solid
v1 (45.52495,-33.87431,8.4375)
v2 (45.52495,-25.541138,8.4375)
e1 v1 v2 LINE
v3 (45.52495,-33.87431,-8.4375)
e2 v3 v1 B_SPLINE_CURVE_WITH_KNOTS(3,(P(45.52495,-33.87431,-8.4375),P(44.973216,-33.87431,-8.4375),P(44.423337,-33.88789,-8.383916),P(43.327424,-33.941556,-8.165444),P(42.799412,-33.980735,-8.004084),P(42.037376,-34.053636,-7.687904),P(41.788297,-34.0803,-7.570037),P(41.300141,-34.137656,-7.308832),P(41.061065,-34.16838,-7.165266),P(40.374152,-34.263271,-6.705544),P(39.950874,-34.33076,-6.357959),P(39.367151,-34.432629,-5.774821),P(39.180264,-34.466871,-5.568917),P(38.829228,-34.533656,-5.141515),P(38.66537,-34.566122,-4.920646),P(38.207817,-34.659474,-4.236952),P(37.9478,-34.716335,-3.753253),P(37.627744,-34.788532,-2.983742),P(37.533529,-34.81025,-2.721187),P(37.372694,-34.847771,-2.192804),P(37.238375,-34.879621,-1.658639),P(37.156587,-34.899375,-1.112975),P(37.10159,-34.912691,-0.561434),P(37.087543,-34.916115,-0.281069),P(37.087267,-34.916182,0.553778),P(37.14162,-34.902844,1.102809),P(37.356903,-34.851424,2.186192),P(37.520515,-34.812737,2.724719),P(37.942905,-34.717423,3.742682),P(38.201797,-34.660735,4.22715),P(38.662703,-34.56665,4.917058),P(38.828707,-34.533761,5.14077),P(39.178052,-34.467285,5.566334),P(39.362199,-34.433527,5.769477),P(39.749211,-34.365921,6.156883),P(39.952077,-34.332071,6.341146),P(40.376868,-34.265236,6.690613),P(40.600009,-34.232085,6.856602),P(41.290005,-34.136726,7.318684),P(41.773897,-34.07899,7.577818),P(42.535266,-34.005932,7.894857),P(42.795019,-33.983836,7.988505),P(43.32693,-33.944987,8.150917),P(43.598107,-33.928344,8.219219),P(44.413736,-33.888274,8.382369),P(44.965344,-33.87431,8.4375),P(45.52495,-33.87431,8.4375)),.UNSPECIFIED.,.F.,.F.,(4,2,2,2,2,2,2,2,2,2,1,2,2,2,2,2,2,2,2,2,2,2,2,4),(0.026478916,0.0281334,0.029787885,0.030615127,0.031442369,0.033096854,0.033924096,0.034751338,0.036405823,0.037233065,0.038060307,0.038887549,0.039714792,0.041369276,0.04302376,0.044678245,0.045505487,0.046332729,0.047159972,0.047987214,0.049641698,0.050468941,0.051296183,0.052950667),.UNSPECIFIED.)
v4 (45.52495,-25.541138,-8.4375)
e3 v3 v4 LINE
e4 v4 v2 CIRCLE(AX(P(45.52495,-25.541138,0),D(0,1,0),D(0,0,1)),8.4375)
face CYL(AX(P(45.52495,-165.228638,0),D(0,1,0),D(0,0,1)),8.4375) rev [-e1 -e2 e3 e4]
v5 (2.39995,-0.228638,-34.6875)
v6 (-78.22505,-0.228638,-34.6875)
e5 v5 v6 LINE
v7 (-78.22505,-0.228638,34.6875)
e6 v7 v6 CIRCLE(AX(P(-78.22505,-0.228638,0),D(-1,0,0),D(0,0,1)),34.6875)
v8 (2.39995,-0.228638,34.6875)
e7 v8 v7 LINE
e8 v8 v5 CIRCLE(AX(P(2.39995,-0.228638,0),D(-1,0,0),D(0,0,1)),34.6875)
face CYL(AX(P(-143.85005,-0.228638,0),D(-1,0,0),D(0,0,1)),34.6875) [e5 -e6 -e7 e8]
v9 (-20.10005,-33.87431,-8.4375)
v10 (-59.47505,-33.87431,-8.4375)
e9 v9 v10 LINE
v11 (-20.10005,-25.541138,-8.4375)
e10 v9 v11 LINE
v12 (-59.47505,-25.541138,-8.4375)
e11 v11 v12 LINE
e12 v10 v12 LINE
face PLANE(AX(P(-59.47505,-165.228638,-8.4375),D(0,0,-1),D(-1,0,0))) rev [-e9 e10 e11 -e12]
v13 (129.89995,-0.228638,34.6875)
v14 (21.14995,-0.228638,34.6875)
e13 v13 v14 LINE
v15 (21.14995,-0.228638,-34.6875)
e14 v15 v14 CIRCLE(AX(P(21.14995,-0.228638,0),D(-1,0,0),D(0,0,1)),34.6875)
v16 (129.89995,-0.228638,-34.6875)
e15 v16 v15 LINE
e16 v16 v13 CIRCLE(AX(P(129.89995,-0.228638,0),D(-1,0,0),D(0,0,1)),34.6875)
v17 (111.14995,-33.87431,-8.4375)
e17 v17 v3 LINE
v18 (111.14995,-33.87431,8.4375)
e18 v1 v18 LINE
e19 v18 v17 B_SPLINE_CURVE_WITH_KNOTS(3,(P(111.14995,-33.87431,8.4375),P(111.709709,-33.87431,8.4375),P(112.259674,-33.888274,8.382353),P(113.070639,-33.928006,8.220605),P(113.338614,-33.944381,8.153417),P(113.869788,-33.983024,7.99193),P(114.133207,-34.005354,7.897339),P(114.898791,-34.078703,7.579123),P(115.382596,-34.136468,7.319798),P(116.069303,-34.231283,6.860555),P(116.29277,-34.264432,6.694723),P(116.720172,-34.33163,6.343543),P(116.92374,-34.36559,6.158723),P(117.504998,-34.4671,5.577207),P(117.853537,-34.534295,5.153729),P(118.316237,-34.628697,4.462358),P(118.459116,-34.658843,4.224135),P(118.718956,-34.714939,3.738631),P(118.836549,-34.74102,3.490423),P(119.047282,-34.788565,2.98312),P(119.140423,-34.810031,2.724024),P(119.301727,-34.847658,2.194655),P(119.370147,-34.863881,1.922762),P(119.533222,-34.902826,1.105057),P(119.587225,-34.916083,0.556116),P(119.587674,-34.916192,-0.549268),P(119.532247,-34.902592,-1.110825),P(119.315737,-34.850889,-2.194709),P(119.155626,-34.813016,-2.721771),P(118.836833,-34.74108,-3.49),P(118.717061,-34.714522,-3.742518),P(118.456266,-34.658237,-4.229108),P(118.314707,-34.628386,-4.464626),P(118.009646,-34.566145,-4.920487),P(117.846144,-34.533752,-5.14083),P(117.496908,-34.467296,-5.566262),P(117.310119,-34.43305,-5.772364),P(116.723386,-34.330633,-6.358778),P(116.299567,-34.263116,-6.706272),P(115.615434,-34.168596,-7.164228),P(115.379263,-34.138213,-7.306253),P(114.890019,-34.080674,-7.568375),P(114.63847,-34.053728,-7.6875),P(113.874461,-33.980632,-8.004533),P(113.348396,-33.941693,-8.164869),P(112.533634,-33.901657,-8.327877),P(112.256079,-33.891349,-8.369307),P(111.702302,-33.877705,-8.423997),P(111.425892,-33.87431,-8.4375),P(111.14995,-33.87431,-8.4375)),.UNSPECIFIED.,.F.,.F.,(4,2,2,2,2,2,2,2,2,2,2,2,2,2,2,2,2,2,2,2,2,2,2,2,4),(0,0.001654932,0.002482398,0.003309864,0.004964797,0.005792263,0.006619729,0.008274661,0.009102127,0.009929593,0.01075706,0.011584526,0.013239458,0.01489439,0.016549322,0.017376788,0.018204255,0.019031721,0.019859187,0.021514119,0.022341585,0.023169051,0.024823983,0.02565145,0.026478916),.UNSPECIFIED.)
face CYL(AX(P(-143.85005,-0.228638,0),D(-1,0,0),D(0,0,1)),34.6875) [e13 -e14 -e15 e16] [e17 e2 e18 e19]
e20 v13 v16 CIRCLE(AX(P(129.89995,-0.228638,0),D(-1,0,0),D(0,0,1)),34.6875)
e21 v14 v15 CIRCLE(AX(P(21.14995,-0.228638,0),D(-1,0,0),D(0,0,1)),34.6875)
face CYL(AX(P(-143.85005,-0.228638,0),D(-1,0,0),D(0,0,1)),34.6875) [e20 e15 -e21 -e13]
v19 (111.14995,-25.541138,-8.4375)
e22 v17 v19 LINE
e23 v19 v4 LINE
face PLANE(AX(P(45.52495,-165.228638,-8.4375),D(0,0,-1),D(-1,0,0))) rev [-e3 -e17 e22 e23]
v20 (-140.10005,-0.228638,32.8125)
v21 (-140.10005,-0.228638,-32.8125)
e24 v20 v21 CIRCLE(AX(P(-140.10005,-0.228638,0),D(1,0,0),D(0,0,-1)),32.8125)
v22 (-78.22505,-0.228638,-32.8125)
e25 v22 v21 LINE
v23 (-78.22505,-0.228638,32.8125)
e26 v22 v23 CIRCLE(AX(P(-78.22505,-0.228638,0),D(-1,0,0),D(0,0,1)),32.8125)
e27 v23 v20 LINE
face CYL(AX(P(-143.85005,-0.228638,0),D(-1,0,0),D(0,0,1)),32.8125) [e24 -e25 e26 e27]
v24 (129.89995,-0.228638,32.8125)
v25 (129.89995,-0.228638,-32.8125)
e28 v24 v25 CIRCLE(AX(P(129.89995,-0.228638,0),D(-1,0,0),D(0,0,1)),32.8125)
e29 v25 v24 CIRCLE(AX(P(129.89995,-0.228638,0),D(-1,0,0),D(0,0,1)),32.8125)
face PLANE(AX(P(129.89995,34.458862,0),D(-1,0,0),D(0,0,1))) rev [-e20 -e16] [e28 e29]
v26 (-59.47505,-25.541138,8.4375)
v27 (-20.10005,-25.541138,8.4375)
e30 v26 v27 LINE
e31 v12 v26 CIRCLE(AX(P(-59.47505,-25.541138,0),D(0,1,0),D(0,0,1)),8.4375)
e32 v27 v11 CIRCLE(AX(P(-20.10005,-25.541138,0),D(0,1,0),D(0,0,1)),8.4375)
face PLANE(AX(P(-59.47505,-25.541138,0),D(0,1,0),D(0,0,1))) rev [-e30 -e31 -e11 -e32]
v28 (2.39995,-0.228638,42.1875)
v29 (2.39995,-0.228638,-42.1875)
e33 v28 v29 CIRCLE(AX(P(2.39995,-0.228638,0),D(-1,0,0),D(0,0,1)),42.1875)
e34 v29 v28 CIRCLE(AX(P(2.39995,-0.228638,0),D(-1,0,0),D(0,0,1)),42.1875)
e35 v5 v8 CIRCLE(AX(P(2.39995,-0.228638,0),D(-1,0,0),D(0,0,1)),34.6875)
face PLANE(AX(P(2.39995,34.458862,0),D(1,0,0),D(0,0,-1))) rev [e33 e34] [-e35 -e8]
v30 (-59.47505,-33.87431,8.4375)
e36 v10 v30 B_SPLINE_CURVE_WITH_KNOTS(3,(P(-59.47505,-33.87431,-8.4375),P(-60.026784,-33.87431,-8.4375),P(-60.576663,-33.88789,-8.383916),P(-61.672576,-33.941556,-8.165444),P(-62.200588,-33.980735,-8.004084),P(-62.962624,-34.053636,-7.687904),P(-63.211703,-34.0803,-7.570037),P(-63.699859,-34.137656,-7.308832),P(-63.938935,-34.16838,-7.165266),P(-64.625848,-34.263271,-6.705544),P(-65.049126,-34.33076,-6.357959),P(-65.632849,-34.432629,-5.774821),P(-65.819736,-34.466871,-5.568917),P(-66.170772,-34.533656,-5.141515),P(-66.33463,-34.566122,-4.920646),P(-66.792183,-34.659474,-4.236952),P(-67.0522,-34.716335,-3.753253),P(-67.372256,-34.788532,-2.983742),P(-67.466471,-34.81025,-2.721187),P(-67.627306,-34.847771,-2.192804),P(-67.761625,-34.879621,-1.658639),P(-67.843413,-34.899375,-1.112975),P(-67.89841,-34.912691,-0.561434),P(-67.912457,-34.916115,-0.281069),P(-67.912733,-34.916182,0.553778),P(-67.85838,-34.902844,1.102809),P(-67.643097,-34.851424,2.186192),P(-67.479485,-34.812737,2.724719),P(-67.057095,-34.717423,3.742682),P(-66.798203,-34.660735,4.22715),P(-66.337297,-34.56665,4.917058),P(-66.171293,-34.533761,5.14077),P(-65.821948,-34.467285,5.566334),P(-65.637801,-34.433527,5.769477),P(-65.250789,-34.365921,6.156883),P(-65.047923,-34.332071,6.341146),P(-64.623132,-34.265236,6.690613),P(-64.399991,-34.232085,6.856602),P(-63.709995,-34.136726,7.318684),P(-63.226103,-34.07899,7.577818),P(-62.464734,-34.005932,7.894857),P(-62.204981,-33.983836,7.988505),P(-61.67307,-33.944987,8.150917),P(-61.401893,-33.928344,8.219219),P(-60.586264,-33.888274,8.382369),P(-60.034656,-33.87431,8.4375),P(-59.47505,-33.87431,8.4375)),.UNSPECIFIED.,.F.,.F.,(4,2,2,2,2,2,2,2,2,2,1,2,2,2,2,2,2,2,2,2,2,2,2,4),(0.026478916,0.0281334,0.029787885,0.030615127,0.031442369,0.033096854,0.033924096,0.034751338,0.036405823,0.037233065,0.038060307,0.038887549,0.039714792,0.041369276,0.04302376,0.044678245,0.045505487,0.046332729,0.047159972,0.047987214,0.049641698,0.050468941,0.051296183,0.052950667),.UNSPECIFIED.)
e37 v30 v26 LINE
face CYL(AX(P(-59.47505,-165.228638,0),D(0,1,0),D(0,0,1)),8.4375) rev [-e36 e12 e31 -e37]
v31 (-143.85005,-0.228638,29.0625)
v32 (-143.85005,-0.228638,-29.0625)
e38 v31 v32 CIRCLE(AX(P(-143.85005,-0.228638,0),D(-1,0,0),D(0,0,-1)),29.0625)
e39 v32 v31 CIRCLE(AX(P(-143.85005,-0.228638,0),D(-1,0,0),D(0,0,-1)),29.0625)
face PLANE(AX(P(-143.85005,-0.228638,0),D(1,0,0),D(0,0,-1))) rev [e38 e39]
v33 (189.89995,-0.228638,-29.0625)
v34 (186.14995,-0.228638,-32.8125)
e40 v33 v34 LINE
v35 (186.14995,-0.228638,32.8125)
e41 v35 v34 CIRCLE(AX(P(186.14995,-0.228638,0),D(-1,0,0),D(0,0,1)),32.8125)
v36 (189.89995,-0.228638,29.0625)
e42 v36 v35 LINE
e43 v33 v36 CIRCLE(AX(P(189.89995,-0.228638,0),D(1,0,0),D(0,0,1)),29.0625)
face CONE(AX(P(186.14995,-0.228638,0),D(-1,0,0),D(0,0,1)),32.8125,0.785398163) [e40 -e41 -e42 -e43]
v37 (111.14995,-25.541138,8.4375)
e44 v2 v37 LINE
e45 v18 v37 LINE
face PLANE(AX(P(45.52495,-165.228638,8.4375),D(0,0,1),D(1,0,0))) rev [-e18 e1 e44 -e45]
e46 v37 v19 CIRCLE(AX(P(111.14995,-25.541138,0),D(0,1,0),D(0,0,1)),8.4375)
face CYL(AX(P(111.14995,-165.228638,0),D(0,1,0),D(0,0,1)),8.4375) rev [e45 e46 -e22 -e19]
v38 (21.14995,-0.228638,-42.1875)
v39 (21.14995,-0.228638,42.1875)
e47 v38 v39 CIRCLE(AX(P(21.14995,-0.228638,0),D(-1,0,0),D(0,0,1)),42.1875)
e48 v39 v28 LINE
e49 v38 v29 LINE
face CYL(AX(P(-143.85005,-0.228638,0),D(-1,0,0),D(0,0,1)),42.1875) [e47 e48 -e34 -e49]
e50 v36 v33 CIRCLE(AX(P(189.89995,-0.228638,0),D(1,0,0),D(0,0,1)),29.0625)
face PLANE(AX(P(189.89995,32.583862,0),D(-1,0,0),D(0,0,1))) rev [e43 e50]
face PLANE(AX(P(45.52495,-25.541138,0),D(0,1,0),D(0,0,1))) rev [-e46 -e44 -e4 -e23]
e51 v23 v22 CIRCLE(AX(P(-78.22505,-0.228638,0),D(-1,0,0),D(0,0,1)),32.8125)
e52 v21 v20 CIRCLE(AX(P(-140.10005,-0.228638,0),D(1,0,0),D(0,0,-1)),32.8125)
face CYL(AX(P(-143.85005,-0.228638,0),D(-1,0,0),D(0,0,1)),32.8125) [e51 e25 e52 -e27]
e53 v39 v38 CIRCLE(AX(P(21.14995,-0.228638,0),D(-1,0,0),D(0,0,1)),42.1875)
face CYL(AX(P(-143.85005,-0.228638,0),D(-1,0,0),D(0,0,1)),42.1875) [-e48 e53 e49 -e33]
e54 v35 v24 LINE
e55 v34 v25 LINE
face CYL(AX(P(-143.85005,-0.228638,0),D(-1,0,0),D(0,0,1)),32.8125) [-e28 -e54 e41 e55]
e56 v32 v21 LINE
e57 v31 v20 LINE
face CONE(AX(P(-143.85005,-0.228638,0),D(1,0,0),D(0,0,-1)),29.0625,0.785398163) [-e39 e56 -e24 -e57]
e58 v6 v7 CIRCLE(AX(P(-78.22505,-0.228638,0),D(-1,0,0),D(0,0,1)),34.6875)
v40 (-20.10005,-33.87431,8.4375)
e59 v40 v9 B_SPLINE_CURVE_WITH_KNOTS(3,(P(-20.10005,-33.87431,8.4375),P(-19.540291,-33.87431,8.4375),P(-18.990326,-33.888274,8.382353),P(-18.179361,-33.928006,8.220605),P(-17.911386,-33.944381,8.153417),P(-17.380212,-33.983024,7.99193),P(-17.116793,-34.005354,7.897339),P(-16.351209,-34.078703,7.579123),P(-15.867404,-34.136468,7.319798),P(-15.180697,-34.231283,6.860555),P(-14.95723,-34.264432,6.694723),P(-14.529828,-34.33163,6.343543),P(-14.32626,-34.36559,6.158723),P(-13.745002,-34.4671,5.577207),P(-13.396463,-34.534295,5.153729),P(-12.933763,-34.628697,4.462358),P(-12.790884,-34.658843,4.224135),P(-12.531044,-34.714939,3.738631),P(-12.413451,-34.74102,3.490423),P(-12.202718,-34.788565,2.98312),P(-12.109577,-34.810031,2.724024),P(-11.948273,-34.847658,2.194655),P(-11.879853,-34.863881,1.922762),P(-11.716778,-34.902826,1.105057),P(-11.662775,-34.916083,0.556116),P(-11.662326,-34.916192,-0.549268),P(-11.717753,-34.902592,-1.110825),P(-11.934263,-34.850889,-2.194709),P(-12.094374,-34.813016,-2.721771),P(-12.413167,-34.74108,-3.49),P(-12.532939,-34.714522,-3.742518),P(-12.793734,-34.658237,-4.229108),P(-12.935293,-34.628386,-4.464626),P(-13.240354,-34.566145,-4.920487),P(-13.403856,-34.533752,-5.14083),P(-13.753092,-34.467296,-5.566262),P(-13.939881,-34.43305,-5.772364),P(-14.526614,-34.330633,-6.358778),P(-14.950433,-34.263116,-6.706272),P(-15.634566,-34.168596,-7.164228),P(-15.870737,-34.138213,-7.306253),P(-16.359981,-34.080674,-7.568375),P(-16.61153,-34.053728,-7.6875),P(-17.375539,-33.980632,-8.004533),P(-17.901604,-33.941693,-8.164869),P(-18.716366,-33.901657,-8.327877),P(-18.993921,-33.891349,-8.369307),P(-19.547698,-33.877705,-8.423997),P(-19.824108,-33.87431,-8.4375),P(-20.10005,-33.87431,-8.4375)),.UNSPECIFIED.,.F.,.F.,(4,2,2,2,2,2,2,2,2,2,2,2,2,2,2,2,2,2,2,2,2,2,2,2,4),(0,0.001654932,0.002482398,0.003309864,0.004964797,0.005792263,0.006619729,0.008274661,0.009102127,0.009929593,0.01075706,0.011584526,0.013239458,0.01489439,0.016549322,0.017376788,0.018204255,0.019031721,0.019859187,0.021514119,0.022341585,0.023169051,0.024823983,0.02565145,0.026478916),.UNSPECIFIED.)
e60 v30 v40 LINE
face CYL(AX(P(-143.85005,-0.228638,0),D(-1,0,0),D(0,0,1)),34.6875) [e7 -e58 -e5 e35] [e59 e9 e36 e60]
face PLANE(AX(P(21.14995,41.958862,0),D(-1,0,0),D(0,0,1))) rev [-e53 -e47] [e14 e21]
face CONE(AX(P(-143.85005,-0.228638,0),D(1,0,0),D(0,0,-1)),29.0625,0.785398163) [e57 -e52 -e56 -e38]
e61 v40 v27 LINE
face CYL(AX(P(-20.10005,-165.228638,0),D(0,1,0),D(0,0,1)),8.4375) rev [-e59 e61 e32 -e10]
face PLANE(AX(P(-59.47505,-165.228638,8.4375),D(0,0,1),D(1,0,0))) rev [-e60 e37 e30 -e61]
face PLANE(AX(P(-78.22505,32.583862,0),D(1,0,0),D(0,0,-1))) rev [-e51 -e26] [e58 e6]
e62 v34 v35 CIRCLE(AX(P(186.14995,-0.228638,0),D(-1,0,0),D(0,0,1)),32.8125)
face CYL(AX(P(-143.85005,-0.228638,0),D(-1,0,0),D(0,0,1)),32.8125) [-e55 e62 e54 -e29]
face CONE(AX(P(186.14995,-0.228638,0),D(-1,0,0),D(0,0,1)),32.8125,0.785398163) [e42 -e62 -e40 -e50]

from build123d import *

# Parameters (mm, degrees)
CHAMFER1_SIZE       = 2
CUT_EXTRUDE1_DEPTH  = 88
BOSS_EXTRUDE1_DEPTH = 13.5
SCALE_1_SCALE       = 1.875


with BuildPart() as part:
    # Sketch1 → Revolve1 (revolve)
    with BuildSketch(Plane.XY, mode=Mode.PRIVATE) as revolve1_sk:
        Polygon((-66.093473684, 0), (-66.093473684, 17.5), (-31.093473684, 17.5), (-31.093473684, 18.5), (11.906526316, 18.5), (11.906526316, 22.5), (21.906526316, 22.5), (21.906526316, 18.5), (79.906526316, 18.5), (79.906526316, 17.5), (111.906526316, 17.5), (111.906526316, 0), align=None)
    revolve(revolve1_sk.sketch.rotate(Axis((-66.093473684, 0, 0), (1, 0, 0)), 90), axis=Axis((-66.093473684, 0, 0), (1, 0, 0)))

    # Chamfer1
    chamfer1_edges = [part.edges().sort_by_distance(p)[0] for p in [
        (-66.093473684, 0, -17.5),
        (111.906526316, 0, -17.5),
    ]]
    chamfer(chamfer1_edges, length=CHAMFER1_SIZE)

    # Sketch 2_2 → Cut-Extrude1 (cut)
    with BuildSketch(Plane(origin=(0, 0, 0), x_dir=(1, 0, 0), z_dir=(0, 1, 0))):
        with BuildLine():
            Line((-21.093473684, 4.5), (-0.093473684, 4.5))
            ThreePointArc((-0.093473684, 4.5), (4.406526316, 0), (-0.093473684, -4.5))
            Line((-0.093473684, -4.5), (-21.093473684, -4.5))
            ThreePointArc((-21.093473684, -4.5), (-25.593473684, 0), (-21.093473684, 4.5))
        make_face()
        with BuildLine():
            Line((34.906526316, 4.5), (69.906526316, 4.5))
            ThreePointArc((69.906526316, 4.5), (74.406526316, 0), (69.906526316, -4.5))
            Line((69.906526316, -4.5), (34.906526316, -4.5))
            ThreePointArc((34.906526316, -4.5), (30.406526316, 0), (34.906526316, 4.5))
        make_face()
    extrude(amount=-CUT_EXTRUDE1_DEPTH, mode=Mode.SUBTRACT)

    # Sketch 2_2 2 → Boss-Extrude1 (add)
    with BuildSketch(Plane(origin=(0, 0, 0), x_dir=(1, 0, 0), z_dir=(0, 1, 0))):
        with BuildLine():
            Line((-21.093473684, 4.5), (-0.093473684, 4.5))
            ThreePointArc((-0.093473684, 4.5), (4.406526316, 0), (-0.093473684, -4.5))
            Line((-0.093473684, -4.5), (-21.093473684, -4.5))
            ThreePointArc((-21.093473684, -4.5), (-25.593473684, 0), (-21.093473684, 4.5))
        make_face()
        with BuildLine():
            Line((34.906526316, 4.5), (69.906526316, 4.5))
            ThreePointArc((69.906526316, 4.5), (74.406526316, 0), (69.906526316, -4.5))
            Line((69.906526316, -4.5), (34.906526316, -4.5))
            ThreePointArc((34.906526316, -4.5), (30.406526316, 0), (34.906526316, 4.5))
        make_face()
    extrude(amount=-BOSS_EXTRUDE1_DEPTH)


with BuildPart() as part_1:
    # Scale 1: scaled about (22.77118049, 0.261331354, 1.672e-06)
    add(part.part.scale(SCALE_1_SCALE).moved(Location((-19.924782929, -0.228664935, -1.463e-06))))


solid = part_1.part
